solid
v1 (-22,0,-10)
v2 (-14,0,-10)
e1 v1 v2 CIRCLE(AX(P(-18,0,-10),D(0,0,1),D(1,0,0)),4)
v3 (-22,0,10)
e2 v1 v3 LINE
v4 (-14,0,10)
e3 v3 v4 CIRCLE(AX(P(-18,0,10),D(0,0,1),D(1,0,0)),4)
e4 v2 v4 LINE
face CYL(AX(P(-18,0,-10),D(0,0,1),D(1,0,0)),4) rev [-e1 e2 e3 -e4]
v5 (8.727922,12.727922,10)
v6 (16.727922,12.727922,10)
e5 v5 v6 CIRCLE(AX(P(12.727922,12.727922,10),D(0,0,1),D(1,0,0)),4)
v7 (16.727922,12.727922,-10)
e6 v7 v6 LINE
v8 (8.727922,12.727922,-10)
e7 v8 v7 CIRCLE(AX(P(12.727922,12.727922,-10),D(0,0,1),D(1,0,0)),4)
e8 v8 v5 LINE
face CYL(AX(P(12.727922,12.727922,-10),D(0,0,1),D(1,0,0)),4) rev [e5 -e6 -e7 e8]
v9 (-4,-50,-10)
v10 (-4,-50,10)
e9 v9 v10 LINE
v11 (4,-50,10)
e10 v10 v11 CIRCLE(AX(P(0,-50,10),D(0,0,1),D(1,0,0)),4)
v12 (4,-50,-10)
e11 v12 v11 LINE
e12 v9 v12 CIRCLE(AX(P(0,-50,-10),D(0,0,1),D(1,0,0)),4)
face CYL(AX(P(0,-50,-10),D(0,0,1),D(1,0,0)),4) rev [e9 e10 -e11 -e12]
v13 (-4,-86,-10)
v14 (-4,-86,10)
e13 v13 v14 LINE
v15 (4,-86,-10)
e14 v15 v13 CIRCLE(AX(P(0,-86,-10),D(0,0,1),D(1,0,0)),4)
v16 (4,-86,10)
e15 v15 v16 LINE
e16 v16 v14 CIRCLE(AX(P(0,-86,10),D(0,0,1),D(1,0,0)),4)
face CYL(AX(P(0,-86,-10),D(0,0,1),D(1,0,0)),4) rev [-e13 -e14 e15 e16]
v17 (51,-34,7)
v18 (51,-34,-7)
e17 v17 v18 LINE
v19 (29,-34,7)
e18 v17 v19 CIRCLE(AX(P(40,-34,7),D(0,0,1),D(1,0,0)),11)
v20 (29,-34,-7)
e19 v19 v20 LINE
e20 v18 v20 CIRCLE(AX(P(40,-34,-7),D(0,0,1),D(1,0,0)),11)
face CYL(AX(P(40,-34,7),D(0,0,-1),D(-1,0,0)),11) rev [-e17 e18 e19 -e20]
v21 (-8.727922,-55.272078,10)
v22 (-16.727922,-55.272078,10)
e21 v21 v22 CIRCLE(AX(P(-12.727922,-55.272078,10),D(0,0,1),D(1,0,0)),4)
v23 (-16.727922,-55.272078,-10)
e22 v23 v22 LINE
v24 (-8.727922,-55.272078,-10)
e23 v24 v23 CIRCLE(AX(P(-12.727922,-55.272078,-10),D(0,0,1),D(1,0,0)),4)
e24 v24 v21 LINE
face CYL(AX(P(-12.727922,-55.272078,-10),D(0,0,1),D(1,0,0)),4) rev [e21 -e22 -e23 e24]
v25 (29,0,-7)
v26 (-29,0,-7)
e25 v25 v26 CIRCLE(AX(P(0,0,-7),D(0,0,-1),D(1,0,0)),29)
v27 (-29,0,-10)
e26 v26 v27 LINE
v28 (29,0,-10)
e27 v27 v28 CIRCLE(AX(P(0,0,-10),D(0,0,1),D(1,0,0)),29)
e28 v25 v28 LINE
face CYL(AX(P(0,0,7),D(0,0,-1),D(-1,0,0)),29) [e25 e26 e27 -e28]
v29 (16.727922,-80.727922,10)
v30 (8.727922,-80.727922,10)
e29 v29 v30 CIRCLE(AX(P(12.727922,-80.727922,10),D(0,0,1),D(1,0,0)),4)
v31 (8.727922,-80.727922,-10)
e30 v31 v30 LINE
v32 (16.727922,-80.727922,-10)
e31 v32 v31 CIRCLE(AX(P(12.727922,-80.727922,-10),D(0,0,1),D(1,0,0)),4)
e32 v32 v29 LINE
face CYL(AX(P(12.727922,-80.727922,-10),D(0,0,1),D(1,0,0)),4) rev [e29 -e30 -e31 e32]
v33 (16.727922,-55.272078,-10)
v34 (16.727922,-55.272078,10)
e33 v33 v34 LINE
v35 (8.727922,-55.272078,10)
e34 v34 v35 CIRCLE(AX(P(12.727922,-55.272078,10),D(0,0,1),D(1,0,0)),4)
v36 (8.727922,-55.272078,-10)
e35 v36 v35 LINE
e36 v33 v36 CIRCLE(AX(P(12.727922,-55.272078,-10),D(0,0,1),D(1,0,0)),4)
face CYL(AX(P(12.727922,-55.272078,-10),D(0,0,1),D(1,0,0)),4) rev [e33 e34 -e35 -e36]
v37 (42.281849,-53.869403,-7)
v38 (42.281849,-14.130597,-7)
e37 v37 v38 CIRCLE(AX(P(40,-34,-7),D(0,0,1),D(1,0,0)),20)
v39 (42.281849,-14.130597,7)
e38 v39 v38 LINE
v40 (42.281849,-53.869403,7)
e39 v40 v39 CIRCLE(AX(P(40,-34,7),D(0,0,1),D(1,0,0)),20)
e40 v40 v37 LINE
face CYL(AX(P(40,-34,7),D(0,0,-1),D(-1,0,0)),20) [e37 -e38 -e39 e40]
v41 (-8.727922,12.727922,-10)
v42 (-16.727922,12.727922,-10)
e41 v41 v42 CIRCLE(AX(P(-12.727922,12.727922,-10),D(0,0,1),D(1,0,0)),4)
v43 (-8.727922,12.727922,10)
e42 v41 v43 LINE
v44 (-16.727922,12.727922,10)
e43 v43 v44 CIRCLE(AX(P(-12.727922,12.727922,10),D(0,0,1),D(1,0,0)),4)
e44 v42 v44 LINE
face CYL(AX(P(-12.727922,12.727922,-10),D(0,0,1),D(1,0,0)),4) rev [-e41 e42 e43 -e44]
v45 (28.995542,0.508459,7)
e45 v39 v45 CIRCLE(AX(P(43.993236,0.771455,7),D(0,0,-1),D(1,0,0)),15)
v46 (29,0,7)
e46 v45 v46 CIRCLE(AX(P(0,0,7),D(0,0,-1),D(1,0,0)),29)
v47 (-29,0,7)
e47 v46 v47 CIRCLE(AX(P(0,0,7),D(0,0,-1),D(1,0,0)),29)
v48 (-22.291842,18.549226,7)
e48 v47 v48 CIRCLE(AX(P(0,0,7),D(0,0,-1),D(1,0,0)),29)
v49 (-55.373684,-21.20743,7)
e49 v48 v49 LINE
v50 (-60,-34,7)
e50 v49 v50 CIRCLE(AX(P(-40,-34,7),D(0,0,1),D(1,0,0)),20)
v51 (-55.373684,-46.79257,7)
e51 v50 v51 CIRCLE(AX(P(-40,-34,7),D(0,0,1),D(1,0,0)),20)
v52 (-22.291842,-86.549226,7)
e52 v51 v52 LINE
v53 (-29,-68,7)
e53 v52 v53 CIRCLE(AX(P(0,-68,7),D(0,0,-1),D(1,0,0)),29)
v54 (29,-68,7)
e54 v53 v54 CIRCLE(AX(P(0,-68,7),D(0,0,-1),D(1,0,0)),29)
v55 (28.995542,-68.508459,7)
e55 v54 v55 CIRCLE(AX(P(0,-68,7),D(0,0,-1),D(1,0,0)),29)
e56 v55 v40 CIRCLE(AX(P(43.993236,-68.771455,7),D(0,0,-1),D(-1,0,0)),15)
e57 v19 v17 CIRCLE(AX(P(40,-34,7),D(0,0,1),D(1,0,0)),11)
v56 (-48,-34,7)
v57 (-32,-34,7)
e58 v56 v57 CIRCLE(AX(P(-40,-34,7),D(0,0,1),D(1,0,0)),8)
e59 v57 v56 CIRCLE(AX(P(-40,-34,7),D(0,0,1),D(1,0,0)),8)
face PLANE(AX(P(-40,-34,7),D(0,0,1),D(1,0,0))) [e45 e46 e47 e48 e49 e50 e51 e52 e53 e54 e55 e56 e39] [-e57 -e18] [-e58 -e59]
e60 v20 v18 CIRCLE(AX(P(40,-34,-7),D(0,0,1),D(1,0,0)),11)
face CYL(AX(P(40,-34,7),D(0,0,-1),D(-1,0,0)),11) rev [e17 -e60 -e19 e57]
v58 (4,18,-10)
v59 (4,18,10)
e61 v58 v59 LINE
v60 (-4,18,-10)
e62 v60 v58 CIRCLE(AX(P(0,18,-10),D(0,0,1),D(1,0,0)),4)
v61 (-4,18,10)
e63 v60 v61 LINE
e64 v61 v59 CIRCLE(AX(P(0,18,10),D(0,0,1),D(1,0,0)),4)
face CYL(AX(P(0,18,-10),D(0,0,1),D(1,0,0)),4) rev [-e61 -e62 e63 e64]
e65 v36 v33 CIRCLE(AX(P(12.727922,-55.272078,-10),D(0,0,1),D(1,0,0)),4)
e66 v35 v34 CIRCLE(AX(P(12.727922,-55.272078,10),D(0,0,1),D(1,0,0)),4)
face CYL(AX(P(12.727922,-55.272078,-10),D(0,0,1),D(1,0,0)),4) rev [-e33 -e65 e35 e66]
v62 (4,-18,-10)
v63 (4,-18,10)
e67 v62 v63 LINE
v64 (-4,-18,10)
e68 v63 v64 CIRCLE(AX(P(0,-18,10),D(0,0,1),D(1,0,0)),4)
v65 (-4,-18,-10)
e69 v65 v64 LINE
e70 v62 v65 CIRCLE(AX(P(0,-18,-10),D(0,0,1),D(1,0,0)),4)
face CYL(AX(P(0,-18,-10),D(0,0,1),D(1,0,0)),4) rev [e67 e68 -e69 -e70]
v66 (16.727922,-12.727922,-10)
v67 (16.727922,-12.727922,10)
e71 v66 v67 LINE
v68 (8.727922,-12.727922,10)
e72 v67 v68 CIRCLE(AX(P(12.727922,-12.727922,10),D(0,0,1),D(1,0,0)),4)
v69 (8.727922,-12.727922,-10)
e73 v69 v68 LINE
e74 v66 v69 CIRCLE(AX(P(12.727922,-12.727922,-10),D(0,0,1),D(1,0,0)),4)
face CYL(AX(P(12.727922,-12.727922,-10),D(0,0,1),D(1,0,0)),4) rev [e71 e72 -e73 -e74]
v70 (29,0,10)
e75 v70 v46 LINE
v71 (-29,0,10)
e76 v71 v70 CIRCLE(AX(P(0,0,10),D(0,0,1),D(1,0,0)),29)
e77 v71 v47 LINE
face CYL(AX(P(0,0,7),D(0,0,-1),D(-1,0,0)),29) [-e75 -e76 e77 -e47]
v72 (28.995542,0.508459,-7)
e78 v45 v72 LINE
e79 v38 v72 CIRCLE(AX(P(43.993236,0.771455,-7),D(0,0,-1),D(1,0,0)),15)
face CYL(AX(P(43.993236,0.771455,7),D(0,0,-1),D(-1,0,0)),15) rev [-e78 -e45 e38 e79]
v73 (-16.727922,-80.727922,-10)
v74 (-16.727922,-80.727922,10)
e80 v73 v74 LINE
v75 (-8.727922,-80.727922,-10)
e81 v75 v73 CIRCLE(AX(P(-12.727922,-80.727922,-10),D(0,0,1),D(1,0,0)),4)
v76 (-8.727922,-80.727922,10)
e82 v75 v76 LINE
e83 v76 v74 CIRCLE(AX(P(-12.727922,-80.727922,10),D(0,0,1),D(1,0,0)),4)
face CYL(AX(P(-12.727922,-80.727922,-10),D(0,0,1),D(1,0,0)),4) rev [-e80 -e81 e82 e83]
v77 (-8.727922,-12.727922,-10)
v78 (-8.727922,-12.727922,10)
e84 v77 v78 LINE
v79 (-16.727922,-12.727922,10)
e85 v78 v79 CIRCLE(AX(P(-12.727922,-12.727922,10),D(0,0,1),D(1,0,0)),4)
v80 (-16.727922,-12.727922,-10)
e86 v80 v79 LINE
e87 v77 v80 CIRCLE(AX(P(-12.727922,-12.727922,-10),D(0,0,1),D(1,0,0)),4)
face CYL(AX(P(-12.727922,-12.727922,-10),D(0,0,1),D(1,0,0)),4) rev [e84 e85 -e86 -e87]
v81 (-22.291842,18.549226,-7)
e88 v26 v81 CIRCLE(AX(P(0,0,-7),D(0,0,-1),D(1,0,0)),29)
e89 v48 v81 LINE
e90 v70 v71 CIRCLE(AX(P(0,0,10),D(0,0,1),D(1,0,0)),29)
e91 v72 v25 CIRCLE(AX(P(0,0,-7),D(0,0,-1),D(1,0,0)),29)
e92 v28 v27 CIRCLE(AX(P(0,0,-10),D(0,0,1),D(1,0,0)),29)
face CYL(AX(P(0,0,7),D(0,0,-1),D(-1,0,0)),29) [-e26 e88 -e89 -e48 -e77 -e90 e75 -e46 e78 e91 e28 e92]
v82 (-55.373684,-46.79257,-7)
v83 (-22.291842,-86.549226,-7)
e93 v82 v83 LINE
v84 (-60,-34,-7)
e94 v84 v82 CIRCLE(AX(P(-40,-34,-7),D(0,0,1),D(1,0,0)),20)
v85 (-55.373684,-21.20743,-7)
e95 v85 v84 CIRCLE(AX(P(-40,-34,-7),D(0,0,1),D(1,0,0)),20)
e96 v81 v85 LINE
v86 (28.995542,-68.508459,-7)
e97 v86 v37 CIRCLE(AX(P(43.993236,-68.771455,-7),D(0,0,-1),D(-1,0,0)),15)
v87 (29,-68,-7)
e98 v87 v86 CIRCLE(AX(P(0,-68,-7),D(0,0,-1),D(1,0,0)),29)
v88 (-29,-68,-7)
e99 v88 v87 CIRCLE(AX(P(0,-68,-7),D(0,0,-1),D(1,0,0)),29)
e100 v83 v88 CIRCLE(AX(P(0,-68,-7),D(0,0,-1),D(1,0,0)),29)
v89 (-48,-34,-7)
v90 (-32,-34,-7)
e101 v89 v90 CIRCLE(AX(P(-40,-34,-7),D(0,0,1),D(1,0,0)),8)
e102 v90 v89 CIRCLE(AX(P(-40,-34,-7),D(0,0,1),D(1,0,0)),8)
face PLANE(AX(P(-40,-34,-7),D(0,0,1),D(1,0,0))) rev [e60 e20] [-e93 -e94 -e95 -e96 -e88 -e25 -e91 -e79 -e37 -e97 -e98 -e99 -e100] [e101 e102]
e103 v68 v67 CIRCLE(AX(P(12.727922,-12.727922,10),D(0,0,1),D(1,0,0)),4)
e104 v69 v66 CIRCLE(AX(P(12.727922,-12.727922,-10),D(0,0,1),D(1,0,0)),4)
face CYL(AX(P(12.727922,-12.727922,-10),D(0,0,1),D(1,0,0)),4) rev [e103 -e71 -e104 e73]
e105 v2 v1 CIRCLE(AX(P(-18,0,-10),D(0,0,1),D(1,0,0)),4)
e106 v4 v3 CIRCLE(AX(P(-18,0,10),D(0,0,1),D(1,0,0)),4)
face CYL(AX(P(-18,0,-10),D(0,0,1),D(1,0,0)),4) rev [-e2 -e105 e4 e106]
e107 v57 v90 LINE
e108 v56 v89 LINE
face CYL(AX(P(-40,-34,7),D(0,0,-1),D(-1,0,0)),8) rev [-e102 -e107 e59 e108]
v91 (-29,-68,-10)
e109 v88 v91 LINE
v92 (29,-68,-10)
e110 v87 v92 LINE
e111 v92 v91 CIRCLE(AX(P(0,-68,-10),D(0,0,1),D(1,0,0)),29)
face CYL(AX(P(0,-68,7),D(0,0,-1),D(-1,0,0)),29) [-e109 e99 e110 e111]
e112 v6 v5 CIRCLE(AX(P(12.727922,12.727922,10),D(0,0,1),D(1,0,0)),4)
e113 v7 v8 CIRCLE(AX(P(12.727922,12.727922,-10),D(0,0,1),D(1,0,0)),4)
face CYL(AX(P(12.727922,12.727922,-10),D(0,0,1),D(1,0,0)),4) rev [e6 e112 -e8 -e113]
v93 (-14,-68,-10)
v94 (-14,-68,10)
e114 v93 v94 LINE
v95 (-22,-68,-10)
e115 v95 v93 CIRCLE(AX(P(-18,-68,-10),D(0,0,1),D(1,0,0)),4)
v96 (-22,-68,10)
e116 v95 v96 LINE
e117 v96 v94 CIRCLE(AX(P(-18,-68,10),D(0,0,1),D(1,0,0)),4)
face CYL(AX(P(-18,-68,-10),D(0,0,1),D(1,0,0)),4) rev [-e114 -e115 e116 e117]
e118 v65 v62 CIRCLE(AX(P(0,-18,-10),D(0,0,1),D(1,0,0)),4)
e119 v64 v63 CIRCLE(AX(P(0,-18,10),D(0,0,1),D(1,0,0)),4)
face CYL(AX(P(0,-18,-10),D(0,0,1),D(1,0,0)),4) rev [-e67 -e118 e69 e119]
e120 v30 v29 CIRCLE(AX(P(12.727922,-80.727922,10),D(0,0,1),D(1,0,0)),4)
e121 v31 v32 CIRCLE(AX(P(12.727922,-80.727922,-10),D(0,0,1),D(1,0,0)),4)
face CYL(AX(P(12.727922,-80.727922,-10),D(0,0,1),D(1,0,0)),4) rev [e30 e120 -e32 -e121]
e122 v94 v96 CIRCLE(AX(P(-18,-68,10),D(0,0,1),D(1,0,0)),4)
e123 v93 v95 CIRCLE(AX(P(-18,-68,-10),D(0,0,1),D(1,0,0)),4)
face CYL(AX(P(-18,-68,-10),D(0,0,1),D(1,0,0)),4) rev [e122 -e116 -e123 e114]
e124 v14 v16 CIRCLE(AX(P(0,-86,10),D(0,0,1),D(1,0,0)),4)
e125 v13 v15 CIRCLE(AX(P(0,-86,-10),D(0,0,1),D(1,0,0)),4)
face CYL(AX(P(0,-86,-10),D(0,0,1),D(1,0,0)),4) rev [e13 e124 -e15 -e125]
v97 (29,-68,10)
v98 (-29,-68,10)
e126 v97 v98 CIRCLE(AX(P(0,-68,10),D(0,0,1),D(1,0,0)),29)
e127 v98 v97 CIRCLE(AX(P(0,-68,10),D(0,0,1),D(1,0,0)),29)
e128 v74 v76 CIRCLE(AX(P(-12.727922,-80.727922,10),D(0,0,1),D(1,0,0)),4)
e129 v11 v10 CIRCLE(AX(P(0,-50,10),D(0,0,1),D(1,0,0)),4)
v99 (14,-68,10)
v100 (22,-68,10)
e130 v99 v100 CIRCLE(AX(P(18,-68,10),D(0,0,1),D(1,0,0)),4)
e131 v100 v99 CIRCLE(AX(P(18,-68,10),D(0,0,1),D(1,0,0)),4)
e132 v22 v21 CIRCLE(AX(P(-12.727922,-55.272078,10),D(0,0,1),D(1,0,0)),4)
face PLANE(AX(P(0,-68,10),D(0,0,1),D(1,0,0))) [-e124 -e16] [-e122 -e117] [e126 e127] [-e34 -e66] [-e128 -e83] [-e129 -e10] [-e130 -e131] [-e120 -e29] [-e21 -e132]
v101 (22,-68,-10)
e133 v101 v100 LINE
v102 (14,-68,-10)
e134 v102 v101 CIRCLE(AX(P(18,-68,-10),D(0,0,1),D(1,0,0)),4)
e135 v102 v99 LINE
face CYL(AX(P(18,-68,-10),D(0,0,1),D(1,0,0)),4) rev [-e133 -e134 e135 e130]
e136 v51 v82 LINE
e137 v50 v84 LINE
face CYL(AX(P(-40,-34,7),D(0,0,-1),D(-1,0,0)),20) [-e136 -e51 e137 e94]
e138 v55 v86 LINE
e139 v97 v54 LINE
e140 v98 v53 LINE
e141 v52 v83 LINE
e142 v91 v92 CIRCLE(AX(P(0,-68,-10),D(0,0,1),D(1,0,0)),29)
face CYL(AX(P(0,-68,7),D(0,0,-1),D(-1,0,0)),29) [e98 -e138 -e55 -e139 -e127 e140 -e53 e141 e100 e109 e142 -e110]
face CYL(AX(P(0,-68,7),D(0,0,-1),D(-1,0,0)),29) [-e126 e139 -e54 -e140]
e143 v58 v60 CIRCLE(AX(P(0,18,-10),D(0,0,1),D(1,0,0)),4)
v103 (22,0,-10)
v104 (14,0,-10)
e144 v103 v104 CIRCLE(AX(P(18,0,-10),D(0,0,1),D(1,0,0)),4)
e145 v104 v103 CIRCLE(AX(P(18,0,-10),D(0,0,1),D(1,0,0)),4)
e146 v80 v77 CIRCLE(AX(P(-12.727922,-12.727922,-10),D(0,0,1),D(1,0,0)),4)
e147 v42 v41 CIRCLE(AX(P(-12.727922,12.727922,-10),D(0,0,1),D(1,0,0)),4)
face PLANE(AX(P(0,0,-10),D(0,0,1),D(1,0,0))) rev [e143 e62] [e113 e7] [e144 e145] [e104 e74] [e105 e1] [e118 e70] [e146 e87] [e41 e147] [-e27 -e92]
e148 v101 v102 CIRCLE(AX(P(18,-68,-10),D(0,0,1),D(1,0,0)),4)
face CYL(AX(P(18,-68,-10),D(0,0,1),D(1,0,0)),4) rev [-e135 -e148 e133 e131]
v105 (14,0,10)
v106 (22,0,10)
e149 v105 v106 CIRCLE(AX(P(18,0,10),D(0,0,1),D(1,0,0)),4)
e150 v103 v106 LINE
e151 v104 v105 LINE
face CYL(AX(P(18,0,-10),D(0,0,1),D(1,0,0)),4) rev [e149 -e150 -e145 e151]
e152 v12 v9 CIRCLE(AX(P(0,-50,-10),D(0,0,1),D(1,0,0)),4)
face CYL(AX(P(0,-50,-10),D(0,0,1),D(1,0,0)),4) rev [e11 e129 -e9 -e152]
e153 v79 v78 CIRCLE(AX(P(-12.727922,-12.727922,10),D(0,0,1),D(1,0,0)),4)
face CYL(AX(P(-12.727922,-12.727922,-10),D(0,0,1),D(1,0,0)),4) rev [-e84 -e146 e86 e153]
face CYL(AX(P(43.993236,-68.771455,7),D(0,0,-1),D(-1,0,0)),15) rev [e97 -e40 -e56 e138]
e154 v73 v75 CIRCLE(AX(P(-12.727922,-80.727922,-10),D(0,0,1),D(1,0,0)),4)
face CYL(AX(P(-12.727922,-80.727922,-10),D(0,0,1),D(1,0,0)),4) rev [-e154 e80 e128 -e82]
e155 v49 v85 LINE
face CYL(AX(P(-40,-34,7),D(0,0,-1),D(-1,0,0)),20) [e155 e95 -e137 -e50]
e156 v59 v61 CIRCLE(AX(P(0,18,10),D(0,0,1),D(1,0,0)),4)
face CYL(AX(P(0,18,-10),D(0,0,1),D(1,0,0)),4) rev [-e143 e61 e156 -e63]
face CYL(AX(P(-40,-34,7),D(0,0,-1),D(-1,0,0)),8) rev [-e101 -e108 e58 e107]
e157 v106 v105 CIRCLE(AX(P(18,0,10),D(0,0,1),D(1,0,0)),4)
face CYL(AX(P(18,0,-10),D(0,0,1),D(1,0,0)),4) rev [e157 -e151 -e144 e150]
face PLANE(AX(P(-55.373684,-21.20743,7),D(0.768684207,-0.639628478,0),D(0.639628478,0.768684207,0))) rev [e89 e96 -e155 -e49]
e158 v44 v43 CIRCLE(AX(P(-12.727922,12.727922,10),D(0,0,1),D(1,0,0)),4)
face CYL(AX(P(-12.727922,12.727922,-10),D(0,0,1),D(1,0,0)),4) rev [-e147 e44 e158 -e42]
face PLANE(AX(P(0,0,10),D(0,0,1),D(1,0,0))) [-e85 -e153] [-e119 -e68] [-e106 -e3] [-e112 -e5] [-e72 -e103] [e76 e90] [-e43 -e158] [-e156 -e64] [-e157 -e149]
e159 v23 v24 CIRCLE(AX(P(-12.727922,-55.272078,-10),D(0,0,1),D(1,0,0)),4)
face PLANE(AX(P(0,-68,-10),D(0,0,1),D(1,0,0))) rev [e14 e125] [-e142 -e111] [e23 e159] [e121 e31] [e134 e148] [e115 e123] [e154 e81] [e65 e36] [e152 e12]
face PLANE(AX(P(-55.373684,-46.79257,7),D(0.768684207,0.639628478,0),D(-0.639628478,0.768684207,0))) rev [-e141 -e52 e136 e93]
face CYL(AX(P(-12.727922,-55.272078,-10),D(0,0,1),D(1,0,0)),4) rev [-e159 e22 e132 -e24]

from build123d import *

# Parameters (mm, degrees)
PLATE_PROFILE_SKETCH_R      = 8
PLATE_PROFILE_SKETCH_R_2    = 11
CONNECTING_PLATE_14MM_DEPTH = 7
HUB_BOSSES_SKETCH_R         = 29
HUB_BOSSES_20MM_DEPTH       = 10
BOLT_CIRCLE_HOLES_SKETCH_R  = 4
BOLT_HOLES_2X8X_8_DEPTH     = 116.797237


with BuildPart() as part:
    # Plate Profile Sketch → Connecting Plate 14mm (new, symmetric)
    with BuildSketch(Plane.XY):
        with BuildLine():
            Line((-55.373684, -21.20743), (-22.291842, 18.549226))
            ThreePointArc((-22.291842, 18.549226), (9.623005, 27.35686), (28.995542, 0.508459))
            ThreePointArc((28.995542, 0.508459), (32.885859, -9.309525), (42.281849, -14.130597))
            ThreePointArc((42.281849, -14.130597), (60, -34), (42.281849, -53.869403))
            ThreePointArc((42.281849, -53.869403), (32.885859, -58.690475), (28.995542, -68.508459))
            ThreePointArc((28.995542, -68.508459), (9.623005, -95.35686), (-22.291842, -86.549226))
            Line((-22.291842, -86.549226), (-55.373684, -46.79257))
            ThreePointArc((-55.373684, -46.79257), (-60, -34), (-55.373684, -21.20743))
        make_face()
        with Locations((-40, -34)):
            Circle(PLATE_PROFILE_SKETCH_R, mode=Mode.SUBTRACT)
        with Locations((40, -34)):
            Circle(PLATE_PROFILE_SKETCH_R_2, mode=Mode.SUBTRACT)
    extrude(amount=CONNECTING_PLATE_14MM_DEPTH, both=True)

    # Hub Bosses Sketch → Hub Bosses 20mm (add, symmetric)
    with BuildSketch(Plane.XY):
        Circle(HUB_BOSSES_SKETCH_R)
        with Locations((0, -68)):
            Circle(HUB_BOSSES_SKETCH_R)
    extrude(amount=HUB_BOSSES_20MM_DEPTH, both=True)

    # Bolt Circle Holes Sketch → Bolt Holes 2x8xØ8 (cut, through all)
    with BuildSketch(Plane.XY.offset(10)):
        with Locations((0, 18)):
            Circle(BOLT_CIRCLE_HOLES_SKETCH_R)
        with Locations((12.727922, 12.727922)):
            Circle(BOLT_CIRCLE_HOLES_SKETCH_R)
        with Locations((18, 0)):
            Circle(BOLT_CIRCLE_HOLES_SKETCH_R)
        with Locations((12.727922, -12.727922)):
            Circle(BOLT_CIRCLE_HOLES_SKETCH_R)
        with Locations((0, -18)):
            Circle(BOLT_CIRCLE_HOLES_SKETCH_R)
        with Locations((-12.727922, -12.727922)):
            Circle(BOLT_CIRCLE_HOLES_SKETCH_R)
        with Locations((-18, 0)):
            Circle(BOLT_CIRCLE_HOLES_SKETCH_R)
        with Locations((-12.727922, 12.727922)):
            Circle(BOLT_CIRCLE_HOLES_SKETCH_R)
        with Locations((0, -50)):
            Circle(BOLT_CIRCLE_HOLES_SKETCH_R)
        with Locations((12.727922, -55.272078)):
            Circle(BOLT_CIRCLE_HOLES_SKETCH_R)
        with Locations((18, -68)):
            Circle(BOLT_CIRCLE_HOLES_SKETCH_R)
        with Locations((12.727922, -80.727922)):
            Circle(BOLT_CIRCLE_HOLES_SKETCH_R)
        with Locations((0, -86)):
            Circle(BOLT_CIRCLE_HOLES_SKETCH_R)
        with Locations((-12.727922, -80.727922)):
            Circle(BOLT_CIRCLE_HOLES_SKETCH_R)
        with Locations((-18, -68)):
            Circle(BOLT_CIRCLE_HOLES_SKETCH_R)
        with Locations((-12.727922, -55.272078)):
            Circle(BOLT_CIRCLE_HOLES_SKETCH_R)
    extrude(amount=-BOLT_HOLES_2X8X_8_DEPTH, mode=Mode.SUBTRACT)


solid = part.part
